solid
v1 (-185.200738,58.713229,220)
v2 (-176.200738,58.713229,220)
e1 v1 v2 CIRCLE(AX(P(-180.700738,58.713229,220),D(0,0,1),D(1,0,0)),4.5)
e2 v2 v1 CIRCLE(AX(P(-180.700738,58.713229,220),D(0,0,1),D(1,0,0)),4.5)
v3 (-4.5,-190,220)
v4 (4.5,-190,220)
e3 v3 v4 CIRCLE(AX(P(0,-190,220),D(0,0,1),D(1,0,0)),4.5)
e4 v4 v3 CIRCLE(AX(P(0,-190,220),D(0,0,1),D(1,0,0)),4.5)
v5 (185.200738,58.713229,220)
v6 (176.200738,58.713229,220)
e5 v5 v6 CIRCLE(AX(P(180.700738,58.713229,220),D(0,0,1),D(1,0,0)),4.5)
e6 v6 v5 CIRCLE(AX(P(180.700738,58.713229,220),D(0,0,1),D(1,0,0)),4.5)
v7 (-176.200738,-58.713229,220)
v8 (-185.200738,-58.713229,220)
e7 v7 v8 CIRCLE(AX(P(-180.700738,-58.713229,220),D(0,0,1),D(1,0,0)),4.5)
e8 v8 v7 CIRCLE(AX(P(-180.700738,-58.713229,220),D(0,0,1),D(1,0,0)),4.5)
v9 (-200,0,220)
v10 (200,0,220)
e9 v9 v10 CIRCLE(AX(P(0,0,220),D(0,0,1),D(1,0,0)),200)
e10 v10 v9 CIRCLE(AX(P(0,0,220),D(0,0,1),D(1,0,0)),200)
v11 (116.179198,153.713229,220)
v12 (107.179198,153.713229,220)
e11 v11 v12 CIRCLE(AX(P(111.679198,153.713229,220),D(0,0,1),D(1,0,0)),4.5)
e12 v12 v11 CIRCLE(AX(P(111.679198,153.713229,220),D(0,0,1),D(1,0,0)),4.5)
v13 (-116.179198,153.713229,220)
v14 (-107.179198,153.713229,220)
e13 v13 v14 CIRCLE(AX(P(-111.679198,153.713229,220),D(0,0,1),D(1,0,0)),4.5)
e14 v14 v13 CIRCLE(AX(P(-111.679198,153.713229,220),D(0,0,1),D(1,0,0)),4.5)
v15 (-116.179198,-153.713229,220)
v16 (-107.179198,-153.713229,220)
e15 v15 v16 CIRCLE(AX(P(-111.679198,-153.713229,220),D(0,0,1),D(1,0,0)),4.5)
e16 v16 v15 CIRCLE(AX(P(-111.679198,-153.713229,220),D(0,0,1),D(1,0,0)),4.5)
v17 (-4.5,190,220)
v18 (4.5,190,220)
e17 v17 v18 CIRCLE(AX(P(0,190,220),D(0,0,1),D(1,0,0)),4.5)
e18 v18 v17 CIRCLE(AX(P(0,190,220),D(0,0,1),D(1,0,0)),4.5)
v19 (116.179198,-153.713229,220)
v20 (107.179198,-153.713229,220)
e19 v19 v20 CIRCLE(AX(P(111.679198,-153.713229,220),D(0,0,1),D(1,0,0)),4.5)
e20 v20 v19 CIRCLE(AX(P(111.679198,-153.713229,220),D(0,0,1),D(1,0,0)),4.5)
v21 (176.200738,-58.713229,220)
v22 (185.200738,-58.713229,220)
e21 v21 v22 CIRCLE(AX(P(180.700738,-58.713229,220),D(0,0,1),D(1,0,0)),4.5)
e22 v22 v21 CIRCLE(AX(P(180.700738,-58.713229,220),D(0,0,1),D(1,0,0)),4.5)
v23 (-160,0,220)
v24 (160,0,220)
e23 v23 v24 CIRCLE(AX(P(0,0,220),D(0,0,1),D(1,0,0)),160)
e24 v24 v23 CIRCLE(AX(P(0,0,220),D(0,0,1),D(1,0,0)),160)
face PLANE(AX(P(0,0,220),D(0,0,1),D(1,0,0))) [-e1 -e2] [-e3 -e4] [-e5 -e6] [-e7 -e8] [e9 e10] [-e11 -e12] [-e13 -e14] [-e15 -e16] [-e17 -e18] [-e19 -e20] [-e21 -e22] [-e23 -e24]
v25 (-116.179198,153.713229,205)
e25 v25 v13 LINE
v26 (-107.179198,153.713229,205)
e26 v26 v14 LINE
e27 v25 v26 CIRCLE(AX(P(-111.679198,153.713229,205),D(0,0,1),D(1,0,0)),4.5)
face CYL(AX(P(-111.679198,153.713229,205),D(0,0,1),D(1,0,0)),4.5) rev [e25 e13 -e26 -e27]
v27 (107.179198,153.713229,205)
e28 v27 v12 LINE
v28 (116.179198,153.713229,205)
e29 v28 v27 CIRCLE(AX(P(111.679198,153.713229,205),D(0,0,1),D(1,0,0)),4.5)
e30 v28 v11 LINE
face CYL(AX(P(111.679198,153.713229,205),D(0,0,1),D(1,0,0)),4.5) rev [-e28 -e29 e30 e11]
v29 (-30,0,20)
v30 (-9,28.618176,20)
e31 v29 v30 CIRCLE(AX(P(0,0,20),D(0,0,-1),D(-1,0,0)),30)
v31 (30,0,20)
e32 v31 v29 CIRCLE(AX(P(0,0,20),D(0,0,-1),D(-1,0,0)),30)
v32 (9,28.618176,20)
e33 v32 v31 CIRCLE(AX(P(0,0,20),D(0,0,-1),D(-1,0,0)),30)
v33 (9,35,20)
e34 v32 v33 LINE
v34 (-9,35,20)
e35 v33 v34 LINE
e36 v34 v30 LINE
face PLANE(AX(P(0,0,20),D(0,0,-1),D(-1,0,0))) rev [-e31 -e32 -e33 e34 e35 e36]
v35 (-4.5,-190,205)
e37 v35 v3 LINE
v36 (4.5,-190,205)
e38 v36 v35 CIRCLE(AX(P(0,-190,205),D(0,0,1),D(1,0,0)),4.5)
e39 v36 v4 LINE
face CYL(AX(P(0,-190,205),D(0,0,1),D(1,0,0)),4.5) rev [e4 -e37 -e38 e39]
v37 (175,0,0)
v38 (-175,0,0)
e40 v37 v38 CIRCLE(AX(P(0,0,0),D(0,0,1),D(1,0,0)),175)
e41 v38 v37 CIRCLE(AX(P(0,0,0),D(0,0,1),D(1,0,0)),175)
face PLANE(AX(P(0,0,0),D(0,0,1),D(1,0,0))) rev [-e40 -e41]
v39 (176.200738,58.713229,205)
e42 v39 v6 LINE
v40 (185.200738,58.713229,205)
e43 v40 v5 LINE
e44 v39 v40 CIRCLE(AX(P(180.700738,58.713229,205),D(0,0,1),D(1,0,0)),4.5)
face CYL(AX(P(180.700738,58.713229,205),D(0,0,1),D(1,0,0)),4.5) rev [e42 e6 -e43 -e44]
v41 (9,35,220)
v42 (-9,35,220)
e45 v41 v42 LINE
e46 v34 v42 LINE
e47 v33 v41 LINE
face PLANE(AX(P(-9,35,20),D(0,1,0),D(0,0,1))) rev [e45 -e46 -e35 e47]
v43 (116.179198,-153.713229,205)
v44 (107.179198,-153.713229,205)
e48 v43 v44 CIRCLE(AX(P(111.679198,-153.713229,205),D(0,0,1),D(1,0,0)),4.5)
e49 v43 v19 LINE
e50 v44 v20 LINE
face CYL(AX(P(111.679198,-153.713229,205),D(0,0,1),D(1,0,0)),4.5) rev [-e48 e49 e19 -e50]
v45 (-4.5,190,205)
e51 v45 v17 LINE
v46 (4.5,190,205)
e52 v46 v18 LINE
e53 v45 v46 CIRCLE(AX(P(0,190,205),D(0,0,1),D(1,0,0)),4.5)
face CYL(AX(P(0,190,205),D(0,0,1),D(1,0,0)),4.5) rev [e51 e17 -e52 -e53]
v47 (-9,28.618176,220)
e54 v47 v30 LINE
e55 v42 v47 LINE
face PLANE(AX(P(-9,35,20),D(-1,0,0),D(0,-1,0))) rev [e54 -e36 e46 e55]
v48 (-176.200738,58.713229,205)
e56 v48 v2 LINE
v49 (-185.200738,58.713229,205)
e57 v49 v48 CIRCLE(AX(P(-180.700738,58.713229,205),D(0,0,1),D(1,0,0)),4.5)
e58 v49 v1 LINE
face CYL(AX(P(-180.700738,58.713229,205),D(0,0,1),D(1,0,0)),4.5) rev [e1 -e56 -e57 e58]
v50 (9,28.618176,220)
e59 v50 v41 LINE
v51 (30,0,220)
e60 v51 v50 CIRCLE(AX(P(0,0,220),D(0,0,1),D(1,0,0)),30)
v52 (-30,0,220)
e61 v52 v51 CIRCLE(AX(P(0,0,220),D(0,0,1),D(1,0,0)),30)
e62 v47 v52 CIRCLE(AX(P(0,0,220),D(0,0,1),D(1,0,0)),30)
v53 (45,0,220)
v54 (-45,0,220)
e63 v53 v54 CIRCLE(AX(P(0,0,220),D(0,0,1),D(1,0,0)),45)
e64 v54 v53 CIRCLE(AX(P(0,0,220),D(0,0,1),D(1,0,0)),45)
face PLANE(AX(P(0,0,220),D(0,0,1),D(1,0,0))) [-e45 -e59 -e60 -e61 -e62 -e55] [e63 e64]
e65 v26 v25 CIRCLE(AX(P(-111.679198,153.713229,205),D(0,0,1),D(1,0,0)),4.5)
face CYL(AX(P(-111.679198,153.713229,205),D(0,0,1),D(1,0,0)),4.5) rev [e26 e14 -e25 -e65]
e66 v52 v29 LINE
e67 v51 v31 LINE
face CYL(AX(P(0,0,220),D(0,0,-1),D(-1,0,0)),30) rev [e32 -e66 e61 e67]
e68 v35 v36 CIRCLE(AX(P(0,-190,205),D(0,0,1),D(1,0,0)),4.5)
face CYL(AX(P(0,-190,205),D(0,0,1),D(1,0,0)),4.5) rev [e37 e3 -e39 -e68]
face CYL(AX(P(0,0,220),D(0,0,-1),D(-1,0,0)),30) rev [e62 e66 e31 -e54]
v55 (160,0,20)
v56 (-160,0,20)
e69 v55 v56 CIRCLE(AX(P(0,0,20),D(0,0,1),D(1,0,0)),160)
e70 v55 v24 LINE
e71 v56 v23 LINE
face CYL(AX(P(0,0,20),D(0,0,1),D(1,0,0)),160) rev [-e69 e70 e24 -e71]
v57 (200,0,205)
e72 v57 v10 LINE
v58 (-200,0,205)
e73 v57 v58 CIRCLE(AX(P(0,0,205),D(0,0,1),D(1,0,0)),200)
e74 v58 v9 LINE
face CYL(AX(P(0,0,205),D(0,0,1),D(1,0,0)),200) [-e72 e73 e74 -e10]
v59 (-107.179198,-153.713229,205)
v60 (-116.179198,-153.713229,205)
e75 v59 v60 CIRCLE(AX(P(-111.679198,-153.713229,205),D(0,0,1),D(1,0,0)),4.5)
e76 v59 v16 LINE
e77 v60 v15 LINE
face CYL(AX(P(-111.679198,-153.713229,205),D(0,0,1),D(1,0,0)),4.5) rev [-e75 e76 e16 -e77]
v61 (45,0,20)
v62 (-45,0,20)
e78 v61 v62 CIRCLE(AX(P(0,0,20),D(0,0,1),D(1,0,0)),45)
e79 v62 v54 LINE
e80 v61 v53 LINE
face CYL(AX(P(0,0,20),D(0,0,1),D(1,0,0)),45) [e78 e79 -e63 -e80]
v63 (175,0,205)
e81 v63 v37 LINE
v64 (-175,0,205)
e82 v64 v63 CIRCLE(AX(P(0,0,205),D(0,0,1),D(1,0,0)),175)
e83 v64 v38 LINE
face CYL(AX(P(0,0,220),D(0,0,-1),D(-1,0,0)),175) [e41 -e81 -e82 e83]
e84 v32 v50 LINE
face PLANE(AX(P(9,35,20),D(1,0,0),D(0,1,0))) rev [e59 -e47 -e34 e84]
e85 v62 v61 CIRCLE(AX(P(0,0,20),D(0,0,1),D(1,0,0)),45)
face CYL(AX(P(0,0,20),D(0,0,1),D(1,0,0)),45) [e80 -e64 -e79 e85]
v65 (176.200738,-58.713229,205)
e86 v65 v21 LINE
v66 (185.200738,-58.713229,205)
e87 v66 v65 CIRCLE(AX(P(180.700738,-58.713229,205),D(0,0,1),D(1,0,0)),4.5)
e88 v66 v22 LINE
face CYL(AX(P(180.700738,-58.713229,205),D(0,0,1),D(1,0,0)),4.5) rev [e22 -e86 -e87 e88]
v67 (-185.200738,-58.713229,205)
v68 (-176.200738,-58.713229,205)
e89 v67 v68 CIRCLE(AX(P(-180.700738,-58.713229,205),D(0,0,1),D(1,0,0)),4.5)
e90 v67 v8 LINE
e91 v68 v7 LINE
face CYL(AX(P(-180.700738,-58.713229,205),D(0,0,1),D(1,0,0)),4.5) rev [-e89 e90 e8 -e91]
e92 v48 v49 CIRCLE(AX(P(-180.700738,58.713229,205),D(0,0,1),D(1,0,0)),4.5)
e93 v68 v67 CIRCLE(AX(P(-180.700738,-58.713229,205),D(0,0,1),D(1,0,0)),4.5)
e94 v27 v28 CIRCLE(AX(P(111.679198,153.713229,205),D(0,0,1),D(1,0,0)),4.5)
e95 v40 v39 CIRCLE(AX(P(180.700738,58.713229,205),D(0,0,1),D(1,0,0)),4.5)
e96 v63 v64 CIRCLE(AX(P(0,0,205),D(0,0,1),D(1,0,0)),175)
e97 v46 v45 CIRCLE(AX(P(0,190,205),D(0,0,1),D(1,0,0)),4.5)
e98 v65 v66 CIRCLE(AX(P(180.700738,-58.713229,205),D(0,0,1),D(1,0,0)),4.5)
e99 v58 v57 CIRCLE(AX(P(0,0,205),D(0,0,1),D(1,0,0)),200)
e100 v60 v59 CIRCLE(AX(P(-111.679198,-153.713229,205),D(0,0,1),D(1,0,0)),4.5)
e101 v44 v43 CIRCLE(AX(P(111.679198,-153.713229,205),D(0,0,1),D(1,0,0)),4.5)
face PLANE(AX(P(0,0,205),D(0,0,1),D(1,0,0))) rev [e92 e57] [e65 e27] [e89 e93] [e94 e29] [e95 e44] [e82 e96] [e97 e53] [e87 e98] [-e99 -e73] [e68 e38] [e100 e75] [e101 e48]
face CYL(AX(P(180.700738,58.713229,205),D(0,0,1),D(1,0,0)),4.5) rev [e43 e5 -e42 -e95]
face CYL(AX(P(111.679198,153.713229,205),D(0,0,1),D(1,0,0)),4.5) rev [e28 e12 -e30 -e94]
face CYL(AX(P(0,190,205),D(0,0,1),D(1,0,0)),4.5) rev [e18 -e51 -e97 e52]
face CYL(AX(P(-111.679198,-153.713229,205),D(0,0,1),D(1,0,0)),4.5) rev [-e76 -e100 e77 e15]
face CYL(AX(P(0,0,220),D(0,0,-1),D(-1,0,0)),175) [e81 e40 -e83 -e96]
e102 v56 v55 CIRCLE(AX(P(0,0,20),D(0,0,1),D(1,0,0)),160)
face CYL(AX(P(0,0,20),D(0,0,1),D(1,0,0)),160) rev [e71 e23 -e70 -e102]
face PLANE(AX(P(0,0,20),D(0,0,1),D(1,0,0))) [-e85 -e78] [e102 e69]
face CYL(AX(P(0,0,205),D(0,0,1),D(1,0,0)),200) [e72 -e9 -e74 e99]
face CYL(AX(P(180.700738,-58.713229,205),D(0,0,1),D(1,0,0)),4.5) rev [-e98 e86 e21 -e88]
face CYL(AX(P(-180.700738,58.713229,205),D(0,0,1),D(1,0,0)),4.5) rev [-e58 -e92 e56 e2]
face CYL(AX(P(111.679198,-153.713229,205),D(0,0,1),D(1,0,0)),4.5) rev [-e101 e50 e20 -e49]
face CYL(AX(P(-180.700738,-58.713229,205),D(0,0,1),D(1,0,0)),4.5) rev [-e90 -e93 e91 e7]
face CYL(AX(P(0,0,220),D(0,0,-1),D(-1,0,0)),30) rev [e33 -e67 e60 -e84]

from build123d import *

# Parameters (mm, degrees)
SKETCH1_R           = 175
SKETCH1_R_2         = 30
BOSS_EXTRUDE1_DEPTH = 220
BOSS_EXTRUDE2_START = -15
SKETCH2_R           = 200
SKETCH2_R_2         = 4.5
SKETCH2_R_3         = 30
BOSS_EXTRUDE2_DEPTH = 15
SKETCH3_R           = 160
SKETCH3_R_2         = 45
CUT_EXTRUDE1_DEPTH  = 200
SKETCH4_R           = 30
BOSS_EXTRUDE3_DEPTH = 20
SKETCH7_W           = 18
SKETCH7_H           = 20.211896708
CUT_EXTRUDE2_DEPTH  = 200


with BuildPart() as part:
    # Sketch1 → Boss-Extrude1 (new body)
    with BuildSketch(Plane.XY):
        Circle(SKETCH1_R)
        Circle(SKETCH1_R_2, mode=Mode.SUBTRACT)
    extrude(amount=BOSS_EXTRUDE1_DEPTH)

    # Sketch2 → Boss-Extrude2 (add)
    with BuildSketch(Plane.XY.offset(220).offset(BOSS_EXTRUDE2_START)):
        Circle(SKETCH2_R)
        with Locations((0, 190)):
            Circle(SKETCH2_R_2, mode=Mode.SUBTRACT)
        with Locations((111.679197936, 153.713228931)):
            Circle(SKETCH2_R_2, mode=Mode.SUBTRACT)
        with Locations((180.700738096, 58.713228931)):
            Circle(SKETCH2_R_2, mode=Mode.SUBTRACT)
        with Locations((180.700738096, -58.713228931)):
            Circle(SKETCH2_R_2, mode=Mode.SUBTRACT)
        with Locations((111.679197936, -153.713228931)):
            Circle(SKETCH2_R_2, mode=Mode.SUBTRACT)
        with Locations((0, -190)):
            Circle(SKETCH2_R_2, mode=Mode.SUBTRACT)
        with Locations((-111.679197936, -153.713228931)):
            Circle(SKETCH2_R_2, mode=Mode.SUBTRACT)
        with Locations((-180.700738096, -58.713228931)):
            Circle(SKETCH2_R_2, mode=Mode.SUBTRACT)
        with Locations((-180.700738096, 58.713228931)):
            Circle(SKETCH2_R_2, mode=Mode.SUBTRACT)
        with Locations((-111.679197936, 153.713228931)):
            Circle(SKETCH2_R_2, mode=Mode.SUBTRACT)
        Circle(SKETCH2_R_3, mode=Mode.SUBTRACT)
    extrude(amount=BOSS_EXTRUDE2_DEPTH)

    # Sketch3 → Cut-Extrude1 (cut)
    with BuildSketch(Plane.XY.offset(220)):
        Circle(SKETCH3_R)
        Circle(SKETCH3_R_2, mode=Mode.SUBTRACT)
    extrude(amount=-CUT_EXTRUDE1_DEPTH, mode=Mode.SUBTRACT)

    # Sketch4 → Boss-Extrude3 (add)
    with BuildSketch(Plane(origin=(0, 0, 0), x_dir=(-1, 0, 0), z_dir=(0, 0, -1))):
        Circle(SKETCH4_R)
    extrude(amount=-BOSS_EXTRUDE3_DEPTH)

    # Sketch7 → Cut-Extrude2 (cut)
    with BuildSketch(Plane.XY.offset(220)):
        with Locations((0, 24.894051646)):
            Rectangle(SKETCH7_W, SKETCH7_H)
    extrude(amount=-CUT_EXTRUDE2_DEPTH, mode=Mode.SUBTRACT)


solid = part.part
